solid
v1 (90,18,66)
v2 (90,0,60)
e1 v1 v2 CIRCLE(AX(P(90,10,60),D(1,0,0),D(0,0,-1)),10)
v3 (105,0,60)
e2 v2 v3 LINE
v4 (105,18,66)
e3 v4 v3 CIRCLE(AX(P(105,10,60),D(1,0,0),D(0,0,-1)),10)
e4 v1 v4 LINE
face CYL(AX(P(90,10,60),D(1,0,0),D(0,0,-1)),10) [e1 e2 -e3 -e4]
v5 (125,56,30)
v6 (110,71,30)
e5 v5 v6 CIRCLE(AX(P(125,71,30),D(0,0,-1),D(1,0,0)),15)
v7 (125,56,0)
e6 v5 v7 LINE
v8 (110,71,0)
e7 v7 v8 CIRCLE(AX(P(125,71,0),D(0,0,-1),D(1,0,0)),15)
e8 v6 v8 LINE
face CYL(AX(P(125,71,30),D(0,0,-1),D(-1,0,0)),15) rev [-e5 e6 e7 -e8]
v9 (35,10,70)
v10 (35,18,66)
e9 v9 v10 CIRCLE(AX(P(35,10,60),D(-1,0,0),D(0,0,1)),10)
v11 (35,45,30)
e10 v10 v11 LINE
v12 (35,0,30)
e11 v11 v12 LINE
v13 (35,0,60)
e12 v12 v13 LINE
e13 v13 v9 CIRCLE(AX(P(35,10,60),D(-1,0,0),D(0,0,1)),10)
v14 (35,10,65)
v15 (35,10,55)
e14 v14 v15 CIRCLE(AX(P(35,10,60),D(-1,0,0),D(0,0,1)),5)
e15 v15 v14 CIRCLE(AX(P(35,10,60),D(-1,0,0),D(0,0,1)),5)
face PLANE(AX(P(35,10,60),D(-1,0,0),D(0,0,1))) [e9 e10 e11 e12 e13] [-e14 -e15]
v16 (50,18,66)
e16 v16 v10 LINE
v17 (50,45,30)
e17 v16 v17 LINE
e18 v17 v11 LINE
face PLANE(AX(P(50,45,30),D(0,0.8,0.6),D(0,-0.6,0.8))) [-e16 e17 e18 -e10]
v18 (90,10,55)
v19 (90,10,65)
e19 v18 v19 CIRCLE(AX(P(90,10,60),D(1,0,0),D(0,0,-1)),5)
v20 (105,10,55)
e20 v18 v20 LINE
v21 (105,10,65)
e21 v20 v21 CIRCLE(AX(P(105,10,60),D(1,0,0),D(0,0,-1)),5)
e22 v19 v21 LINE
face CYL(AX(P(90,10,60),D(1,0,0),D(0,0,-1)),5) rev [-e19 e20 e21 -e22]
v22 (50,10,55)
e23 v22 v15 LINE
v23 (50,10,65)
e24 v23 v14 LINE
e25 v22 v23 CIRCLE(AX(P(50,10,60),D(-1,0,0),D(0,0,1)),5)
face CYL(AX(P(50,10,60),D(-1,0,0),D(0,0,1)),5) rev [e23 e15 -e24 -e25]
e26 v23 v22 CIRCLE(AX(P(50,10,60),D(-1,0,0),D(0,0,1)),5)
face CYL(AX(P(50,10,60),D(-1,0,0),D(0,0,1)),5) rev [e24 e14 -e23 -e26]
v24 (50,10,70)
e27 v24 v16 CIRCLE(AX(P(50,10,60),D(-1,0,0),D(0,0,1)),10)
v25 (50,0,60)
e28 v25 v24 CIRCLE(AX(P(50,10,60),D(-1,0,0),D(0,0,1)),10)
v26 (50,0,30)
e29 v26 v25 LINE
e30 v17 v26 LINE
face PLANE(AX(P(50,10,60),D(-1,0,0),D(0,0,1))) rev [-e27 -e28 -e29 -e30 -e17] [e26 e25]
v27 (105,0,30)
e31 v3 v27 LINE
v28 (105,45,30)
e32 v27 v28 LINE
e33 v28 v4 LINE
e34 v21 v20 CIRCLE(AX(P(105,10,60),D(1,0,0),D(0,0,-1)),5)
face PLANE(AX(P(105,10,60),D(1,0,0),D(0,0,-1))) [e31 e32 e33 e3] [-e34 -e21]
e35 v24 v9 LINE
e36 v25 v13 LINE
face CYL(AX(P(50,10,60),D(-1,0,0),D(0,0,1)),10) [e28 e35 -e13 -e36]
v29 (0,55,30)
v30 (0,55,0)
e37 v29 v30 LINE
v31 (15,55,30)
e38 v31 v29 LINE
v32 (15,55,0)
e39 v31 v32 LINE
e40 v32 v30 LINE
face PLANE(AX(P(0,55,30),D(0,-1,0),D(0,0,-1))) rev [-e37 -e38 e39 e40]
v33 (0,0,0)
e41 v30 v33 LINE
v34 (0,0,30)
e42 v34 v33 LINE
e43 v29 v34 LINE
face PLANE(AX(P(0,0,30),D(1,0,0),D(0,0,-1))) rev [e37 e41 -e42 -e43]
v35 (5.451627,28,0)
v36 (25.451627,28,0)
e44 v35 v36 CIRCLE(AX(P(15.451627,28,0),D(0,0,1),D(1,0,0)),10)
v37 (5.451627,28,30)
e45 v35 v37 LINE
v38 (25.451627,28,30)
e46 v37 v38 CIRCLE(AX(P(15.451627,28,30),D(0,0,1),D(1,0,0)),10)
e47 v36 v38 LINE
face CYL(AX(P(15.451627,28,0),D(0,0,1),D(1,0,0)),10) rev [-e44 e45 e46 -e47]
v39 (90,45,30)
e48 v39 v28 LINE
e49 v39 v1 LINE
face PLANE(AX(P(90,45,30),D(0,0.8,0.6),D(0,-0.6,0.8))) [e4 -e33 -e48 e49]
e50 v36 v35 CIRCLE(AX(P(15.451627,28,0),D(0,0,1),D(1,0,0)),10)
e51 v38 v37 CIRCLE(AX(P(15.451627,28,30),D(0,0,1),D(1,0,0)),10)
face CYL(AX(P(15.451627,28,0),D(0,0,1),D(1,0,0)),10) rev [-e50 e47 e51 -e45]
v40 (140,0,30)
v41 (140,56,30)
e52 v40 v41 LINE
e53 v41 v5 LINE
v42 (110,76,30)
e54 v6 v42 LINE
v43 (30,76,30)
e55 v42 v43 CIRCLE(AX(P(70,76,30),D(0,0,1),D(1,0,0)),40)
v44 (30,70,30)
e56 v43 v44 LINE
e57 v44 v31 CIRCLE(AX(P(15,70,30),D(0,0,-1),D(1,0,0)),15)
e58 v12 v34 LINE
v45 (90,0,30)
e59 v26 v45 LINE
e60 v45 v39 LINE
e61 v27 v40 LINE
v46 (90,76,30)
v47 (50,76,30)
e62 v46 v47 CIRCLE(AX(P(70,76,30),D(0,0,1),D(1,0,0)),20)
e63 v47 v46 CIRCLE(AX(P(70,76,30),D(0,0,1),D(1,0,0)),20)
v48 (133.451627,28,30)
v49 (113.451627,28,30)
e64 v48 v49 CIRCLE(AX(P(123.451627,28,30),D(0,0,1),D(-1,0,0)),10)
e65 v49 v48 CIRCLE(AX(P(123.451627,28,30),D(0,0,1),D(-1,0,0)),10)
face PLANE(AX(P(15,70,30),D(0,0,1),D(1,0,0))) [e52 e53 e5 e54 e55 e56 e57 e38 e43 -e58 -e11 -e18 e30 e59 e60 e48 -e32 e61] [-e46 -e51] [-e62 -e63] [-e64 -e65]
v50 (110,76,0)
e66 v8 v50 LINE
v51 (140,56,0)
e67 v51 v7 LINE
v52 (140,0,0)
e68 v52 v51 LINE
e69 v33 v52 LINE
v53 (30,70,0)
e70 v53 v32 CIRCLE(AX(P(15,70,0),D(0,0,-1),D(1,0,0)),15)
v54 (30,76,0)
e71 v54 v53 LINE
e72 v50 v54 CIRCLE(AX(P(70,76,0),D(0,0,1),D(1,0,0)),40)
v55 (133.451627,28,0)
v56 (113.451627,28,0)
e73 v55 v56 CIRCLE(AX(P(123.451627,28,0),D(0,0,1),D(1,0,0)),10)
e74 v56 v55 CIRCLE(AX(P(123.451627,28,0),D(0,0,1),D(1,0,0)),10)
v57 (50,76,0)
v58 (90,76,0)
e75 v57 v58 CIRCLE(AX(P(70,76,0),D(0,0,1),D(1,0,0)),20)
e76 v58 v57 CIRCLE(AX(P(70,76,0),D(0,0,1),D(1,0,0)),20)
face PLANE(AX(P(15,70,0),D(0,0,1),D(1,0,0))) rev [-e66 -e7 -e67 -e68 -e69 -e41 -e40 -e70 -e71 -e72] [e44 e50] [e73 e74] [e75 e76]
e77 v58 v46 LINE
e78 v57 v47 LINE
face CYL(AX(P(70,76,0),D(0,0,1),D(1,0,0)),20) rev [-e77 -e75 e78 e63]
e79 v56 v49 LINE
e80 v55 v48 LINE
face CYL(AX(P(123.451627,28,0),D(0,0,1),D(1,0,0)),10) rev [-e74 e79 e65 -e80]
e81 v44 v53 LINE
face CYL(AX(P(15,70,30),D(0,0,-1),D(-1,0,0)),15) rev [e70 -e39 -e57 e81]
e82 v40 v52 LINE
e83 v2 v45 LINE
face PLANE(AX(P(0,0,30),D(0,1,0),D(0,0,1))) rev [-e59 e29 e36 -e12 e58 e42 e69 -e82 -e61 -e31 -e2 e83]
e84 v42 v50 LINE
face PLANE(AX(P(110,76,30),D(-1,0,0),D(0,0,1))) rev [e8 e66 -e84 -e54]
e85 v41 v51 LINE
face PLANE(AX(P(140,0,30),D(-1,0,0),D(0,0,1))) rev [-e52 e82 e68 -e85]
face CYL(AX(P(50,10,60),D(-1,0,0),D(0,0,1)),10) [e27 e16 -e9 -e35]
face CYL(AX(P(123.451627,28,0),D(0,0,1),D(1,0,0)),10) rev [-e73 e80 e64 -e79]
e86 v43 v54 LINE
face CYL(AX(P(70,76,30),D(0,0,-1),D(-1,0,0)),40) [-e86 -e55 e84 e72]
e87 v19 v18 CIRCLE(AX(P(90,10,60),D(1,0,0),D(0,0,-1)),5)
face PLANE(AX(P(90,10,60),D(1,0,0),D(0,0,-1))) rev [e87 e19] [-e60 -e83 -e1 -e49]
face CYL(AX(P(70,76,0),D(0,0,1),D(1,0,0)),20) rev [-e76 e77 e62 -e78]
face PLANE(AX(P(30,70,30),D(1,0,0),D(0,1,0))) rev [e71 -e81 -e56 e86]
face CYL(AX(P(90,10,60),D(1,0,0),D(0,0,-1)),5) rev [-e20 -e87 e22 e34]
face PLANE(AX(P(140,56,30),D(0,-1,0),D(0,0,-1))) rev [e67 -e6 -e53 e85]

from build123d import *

# Parameters (mm, degrees)
BASE_PLATE_DEPTH         = 30
CENTER_BORE_PROFILE_R    = 20
CENTER_BORE_DEPTH        = 30
SIDE_HOLES_PROFILE_R     = 10
SIDE_HOLES_2X_28_DEPTH   = 30
LUG_1_DEPTH              = 50
LUG_1_TAPER_CUT_DEPTH    = 35
LUG_1_PIN_HOLE_PROFILE_R = 5
LUG_1_PIN_HOLE_DEPTH     = 15
LUG_START                = -50
LUG_2_DEPTH              = 50
LUG_START_2              = -35
LUG_2_TAPER_CUT_DEPTH    = 35
LUG_START_3              = -15
LUG_2_PIN_HOLE_PROFILE_R = 5
LUG_2_PIN_HOLE_DEPTH     = 15


with BuildPart() as part:
    # Base Plate Profile → Base Plate (new body)
    with BuildSketch(Plane.XY):
        with BuildLine():
            Line((0, 0), (140, 0))
            Line((140, 0), (140, 56))
            Line((140, 56), (125, 56))
            ThreePointArc((125, 56), (114.393398282, 60.393398282), (110, 71))
            Line((110, 71), (110, 76))
            ThreePointArc((110, 76), (70, 116), (30, 76))
            Line((30, 76), (30, 70))
            ThreePointArc((30, 70), (25.606601718, 59.393398282), (15, 55))
            Line((15, 55), (0, 55))
            Line((0, 55), (0, 0))
        make_face()
    extrude(amount=BASE_PLATE_DEPTH)

    # Center Bore Profile → Center Bore (cut)
    with BuildSketch(Plane.XY.offset(30)):
        with Locations((70, 76)):
            Circle(CENTER_BORE_PROFILE_R)
    extrude(amount=-CENTER_BORE_DEPTH, mode=Mode.SUBTRACT)

    # Side Holes Profile → Side Holes 2xØ28 (cut)
    with BuildSketch(Plane.XY.offset(30)):
        with Locations((15.451626978, 28)):
            Circle(SIDE_HOLES_PROFILE_R)
        with Locations((123.451626978, 28)):
            Circle(SIDE_HOLES_PROFILE_R)
    extrude(amount=-SIDE_HOLES_2X_28_DEPTH, mode=Mode.SUBTRACT)

    # Lug 1 Profile → Lug 1 (add)
    with BuildSketch(Plane.ZY):
        with BuildLine():
            Line((30, 0), (30, 45))
            Line((30, 45), (66, 18))
            ThreePointArc((66, 18), (69.486832981, 6.83772234), (60, 0))
            Line((60, 0), (30, 0))
        make_face()
    extrude(amount=-LUG_1_DEPTH)

    # Lug 1 Taper Profile → Lug 1 Taper Cut (cut)
    with BuildSketch(Plane.ZY):
        with BuildLine():
            Line((30, 45), (30, 0))
            Line((30, 0), (60, 0))
            ThreePointArc((60, 0), (69.486832981, 6.83772234), (66, 18))
            Line((66, 18), (30, 45))
        make_face()
    extrude(amount=-LUG_1_TAPER_CUT_DEPTH, mode=Mode.SUBTRACT)

    # Lug 1 Pin Hole Profile → Lug 1 Pin Hole (cut)
    with BuildSketch(Plane.ZY.offset(-35)):
        with Locations((60, 10)):
            Circle(LUG_1_PIN_HOLE_PROFILE_R)
    extrude(amount=-LUG_1_PIN_HOLE_DEPTH, mode=Mode.SUBTRACT)

    # Lug 2 Profile → Lug 2 (add)
    with BuildSketch(Plane(origin=(140, 0, 0), x_dir=(0, 0, -1), z_dir=(1, 0, 0)).offset(LUG_START)):
        with BuildLine():
            Line((-30, 0), (-30, 45))
            Line((-30, 45), (-66, 18))
            ThreePointArc((-66, 18), (-69.486832981, 6.83772234), (-60, 0))
            Line((-60, 0), (-30, 0))
        make_face()
    extrude(amount=LUG_2_DEPTH)

    # Lug 2 Taper Profile → Lug 2 Taper Cut (cut)
    with BuildSketch(Plane(origin=(140, 0, 0), x_dir=(0, 0, -1), z_dir=(1, 0, 0)).offset(LUG_START_2)):
        with BuildLine():
            Line((-30, 45), (-66, 18))
            ThreePointArc((-66, 18), (-69.486832981, 6.83772234), (-60, 0))
            Line((-60, 0), (-30, 0))
            Line((-30, 0), (-30, 45))
        make_face()
    extrude(amount=LUG_2_TAPER_CUT_DEPTH, mode=Mode.SUBTRACT)

    # Lug 2 Pin Hole Profile → Lug 2 Pin Hole (cut)
    with BuildSketch(Plane(origin=(105, 0, 0), x_dir=(0, 0, -1), z_dir=(1, 0, 0)).offset(LUG_START_3)):
        with Locations(Location((-60, 10, 0), (0, 0, 180))):
            Circle(LUG_2_PIN_HOLE_PROFILE_R)
    extrude(amount=LUG_2_PIN_HOLE_DEPTH, mode=Mode.SUBTRACT)


solid = part.part
